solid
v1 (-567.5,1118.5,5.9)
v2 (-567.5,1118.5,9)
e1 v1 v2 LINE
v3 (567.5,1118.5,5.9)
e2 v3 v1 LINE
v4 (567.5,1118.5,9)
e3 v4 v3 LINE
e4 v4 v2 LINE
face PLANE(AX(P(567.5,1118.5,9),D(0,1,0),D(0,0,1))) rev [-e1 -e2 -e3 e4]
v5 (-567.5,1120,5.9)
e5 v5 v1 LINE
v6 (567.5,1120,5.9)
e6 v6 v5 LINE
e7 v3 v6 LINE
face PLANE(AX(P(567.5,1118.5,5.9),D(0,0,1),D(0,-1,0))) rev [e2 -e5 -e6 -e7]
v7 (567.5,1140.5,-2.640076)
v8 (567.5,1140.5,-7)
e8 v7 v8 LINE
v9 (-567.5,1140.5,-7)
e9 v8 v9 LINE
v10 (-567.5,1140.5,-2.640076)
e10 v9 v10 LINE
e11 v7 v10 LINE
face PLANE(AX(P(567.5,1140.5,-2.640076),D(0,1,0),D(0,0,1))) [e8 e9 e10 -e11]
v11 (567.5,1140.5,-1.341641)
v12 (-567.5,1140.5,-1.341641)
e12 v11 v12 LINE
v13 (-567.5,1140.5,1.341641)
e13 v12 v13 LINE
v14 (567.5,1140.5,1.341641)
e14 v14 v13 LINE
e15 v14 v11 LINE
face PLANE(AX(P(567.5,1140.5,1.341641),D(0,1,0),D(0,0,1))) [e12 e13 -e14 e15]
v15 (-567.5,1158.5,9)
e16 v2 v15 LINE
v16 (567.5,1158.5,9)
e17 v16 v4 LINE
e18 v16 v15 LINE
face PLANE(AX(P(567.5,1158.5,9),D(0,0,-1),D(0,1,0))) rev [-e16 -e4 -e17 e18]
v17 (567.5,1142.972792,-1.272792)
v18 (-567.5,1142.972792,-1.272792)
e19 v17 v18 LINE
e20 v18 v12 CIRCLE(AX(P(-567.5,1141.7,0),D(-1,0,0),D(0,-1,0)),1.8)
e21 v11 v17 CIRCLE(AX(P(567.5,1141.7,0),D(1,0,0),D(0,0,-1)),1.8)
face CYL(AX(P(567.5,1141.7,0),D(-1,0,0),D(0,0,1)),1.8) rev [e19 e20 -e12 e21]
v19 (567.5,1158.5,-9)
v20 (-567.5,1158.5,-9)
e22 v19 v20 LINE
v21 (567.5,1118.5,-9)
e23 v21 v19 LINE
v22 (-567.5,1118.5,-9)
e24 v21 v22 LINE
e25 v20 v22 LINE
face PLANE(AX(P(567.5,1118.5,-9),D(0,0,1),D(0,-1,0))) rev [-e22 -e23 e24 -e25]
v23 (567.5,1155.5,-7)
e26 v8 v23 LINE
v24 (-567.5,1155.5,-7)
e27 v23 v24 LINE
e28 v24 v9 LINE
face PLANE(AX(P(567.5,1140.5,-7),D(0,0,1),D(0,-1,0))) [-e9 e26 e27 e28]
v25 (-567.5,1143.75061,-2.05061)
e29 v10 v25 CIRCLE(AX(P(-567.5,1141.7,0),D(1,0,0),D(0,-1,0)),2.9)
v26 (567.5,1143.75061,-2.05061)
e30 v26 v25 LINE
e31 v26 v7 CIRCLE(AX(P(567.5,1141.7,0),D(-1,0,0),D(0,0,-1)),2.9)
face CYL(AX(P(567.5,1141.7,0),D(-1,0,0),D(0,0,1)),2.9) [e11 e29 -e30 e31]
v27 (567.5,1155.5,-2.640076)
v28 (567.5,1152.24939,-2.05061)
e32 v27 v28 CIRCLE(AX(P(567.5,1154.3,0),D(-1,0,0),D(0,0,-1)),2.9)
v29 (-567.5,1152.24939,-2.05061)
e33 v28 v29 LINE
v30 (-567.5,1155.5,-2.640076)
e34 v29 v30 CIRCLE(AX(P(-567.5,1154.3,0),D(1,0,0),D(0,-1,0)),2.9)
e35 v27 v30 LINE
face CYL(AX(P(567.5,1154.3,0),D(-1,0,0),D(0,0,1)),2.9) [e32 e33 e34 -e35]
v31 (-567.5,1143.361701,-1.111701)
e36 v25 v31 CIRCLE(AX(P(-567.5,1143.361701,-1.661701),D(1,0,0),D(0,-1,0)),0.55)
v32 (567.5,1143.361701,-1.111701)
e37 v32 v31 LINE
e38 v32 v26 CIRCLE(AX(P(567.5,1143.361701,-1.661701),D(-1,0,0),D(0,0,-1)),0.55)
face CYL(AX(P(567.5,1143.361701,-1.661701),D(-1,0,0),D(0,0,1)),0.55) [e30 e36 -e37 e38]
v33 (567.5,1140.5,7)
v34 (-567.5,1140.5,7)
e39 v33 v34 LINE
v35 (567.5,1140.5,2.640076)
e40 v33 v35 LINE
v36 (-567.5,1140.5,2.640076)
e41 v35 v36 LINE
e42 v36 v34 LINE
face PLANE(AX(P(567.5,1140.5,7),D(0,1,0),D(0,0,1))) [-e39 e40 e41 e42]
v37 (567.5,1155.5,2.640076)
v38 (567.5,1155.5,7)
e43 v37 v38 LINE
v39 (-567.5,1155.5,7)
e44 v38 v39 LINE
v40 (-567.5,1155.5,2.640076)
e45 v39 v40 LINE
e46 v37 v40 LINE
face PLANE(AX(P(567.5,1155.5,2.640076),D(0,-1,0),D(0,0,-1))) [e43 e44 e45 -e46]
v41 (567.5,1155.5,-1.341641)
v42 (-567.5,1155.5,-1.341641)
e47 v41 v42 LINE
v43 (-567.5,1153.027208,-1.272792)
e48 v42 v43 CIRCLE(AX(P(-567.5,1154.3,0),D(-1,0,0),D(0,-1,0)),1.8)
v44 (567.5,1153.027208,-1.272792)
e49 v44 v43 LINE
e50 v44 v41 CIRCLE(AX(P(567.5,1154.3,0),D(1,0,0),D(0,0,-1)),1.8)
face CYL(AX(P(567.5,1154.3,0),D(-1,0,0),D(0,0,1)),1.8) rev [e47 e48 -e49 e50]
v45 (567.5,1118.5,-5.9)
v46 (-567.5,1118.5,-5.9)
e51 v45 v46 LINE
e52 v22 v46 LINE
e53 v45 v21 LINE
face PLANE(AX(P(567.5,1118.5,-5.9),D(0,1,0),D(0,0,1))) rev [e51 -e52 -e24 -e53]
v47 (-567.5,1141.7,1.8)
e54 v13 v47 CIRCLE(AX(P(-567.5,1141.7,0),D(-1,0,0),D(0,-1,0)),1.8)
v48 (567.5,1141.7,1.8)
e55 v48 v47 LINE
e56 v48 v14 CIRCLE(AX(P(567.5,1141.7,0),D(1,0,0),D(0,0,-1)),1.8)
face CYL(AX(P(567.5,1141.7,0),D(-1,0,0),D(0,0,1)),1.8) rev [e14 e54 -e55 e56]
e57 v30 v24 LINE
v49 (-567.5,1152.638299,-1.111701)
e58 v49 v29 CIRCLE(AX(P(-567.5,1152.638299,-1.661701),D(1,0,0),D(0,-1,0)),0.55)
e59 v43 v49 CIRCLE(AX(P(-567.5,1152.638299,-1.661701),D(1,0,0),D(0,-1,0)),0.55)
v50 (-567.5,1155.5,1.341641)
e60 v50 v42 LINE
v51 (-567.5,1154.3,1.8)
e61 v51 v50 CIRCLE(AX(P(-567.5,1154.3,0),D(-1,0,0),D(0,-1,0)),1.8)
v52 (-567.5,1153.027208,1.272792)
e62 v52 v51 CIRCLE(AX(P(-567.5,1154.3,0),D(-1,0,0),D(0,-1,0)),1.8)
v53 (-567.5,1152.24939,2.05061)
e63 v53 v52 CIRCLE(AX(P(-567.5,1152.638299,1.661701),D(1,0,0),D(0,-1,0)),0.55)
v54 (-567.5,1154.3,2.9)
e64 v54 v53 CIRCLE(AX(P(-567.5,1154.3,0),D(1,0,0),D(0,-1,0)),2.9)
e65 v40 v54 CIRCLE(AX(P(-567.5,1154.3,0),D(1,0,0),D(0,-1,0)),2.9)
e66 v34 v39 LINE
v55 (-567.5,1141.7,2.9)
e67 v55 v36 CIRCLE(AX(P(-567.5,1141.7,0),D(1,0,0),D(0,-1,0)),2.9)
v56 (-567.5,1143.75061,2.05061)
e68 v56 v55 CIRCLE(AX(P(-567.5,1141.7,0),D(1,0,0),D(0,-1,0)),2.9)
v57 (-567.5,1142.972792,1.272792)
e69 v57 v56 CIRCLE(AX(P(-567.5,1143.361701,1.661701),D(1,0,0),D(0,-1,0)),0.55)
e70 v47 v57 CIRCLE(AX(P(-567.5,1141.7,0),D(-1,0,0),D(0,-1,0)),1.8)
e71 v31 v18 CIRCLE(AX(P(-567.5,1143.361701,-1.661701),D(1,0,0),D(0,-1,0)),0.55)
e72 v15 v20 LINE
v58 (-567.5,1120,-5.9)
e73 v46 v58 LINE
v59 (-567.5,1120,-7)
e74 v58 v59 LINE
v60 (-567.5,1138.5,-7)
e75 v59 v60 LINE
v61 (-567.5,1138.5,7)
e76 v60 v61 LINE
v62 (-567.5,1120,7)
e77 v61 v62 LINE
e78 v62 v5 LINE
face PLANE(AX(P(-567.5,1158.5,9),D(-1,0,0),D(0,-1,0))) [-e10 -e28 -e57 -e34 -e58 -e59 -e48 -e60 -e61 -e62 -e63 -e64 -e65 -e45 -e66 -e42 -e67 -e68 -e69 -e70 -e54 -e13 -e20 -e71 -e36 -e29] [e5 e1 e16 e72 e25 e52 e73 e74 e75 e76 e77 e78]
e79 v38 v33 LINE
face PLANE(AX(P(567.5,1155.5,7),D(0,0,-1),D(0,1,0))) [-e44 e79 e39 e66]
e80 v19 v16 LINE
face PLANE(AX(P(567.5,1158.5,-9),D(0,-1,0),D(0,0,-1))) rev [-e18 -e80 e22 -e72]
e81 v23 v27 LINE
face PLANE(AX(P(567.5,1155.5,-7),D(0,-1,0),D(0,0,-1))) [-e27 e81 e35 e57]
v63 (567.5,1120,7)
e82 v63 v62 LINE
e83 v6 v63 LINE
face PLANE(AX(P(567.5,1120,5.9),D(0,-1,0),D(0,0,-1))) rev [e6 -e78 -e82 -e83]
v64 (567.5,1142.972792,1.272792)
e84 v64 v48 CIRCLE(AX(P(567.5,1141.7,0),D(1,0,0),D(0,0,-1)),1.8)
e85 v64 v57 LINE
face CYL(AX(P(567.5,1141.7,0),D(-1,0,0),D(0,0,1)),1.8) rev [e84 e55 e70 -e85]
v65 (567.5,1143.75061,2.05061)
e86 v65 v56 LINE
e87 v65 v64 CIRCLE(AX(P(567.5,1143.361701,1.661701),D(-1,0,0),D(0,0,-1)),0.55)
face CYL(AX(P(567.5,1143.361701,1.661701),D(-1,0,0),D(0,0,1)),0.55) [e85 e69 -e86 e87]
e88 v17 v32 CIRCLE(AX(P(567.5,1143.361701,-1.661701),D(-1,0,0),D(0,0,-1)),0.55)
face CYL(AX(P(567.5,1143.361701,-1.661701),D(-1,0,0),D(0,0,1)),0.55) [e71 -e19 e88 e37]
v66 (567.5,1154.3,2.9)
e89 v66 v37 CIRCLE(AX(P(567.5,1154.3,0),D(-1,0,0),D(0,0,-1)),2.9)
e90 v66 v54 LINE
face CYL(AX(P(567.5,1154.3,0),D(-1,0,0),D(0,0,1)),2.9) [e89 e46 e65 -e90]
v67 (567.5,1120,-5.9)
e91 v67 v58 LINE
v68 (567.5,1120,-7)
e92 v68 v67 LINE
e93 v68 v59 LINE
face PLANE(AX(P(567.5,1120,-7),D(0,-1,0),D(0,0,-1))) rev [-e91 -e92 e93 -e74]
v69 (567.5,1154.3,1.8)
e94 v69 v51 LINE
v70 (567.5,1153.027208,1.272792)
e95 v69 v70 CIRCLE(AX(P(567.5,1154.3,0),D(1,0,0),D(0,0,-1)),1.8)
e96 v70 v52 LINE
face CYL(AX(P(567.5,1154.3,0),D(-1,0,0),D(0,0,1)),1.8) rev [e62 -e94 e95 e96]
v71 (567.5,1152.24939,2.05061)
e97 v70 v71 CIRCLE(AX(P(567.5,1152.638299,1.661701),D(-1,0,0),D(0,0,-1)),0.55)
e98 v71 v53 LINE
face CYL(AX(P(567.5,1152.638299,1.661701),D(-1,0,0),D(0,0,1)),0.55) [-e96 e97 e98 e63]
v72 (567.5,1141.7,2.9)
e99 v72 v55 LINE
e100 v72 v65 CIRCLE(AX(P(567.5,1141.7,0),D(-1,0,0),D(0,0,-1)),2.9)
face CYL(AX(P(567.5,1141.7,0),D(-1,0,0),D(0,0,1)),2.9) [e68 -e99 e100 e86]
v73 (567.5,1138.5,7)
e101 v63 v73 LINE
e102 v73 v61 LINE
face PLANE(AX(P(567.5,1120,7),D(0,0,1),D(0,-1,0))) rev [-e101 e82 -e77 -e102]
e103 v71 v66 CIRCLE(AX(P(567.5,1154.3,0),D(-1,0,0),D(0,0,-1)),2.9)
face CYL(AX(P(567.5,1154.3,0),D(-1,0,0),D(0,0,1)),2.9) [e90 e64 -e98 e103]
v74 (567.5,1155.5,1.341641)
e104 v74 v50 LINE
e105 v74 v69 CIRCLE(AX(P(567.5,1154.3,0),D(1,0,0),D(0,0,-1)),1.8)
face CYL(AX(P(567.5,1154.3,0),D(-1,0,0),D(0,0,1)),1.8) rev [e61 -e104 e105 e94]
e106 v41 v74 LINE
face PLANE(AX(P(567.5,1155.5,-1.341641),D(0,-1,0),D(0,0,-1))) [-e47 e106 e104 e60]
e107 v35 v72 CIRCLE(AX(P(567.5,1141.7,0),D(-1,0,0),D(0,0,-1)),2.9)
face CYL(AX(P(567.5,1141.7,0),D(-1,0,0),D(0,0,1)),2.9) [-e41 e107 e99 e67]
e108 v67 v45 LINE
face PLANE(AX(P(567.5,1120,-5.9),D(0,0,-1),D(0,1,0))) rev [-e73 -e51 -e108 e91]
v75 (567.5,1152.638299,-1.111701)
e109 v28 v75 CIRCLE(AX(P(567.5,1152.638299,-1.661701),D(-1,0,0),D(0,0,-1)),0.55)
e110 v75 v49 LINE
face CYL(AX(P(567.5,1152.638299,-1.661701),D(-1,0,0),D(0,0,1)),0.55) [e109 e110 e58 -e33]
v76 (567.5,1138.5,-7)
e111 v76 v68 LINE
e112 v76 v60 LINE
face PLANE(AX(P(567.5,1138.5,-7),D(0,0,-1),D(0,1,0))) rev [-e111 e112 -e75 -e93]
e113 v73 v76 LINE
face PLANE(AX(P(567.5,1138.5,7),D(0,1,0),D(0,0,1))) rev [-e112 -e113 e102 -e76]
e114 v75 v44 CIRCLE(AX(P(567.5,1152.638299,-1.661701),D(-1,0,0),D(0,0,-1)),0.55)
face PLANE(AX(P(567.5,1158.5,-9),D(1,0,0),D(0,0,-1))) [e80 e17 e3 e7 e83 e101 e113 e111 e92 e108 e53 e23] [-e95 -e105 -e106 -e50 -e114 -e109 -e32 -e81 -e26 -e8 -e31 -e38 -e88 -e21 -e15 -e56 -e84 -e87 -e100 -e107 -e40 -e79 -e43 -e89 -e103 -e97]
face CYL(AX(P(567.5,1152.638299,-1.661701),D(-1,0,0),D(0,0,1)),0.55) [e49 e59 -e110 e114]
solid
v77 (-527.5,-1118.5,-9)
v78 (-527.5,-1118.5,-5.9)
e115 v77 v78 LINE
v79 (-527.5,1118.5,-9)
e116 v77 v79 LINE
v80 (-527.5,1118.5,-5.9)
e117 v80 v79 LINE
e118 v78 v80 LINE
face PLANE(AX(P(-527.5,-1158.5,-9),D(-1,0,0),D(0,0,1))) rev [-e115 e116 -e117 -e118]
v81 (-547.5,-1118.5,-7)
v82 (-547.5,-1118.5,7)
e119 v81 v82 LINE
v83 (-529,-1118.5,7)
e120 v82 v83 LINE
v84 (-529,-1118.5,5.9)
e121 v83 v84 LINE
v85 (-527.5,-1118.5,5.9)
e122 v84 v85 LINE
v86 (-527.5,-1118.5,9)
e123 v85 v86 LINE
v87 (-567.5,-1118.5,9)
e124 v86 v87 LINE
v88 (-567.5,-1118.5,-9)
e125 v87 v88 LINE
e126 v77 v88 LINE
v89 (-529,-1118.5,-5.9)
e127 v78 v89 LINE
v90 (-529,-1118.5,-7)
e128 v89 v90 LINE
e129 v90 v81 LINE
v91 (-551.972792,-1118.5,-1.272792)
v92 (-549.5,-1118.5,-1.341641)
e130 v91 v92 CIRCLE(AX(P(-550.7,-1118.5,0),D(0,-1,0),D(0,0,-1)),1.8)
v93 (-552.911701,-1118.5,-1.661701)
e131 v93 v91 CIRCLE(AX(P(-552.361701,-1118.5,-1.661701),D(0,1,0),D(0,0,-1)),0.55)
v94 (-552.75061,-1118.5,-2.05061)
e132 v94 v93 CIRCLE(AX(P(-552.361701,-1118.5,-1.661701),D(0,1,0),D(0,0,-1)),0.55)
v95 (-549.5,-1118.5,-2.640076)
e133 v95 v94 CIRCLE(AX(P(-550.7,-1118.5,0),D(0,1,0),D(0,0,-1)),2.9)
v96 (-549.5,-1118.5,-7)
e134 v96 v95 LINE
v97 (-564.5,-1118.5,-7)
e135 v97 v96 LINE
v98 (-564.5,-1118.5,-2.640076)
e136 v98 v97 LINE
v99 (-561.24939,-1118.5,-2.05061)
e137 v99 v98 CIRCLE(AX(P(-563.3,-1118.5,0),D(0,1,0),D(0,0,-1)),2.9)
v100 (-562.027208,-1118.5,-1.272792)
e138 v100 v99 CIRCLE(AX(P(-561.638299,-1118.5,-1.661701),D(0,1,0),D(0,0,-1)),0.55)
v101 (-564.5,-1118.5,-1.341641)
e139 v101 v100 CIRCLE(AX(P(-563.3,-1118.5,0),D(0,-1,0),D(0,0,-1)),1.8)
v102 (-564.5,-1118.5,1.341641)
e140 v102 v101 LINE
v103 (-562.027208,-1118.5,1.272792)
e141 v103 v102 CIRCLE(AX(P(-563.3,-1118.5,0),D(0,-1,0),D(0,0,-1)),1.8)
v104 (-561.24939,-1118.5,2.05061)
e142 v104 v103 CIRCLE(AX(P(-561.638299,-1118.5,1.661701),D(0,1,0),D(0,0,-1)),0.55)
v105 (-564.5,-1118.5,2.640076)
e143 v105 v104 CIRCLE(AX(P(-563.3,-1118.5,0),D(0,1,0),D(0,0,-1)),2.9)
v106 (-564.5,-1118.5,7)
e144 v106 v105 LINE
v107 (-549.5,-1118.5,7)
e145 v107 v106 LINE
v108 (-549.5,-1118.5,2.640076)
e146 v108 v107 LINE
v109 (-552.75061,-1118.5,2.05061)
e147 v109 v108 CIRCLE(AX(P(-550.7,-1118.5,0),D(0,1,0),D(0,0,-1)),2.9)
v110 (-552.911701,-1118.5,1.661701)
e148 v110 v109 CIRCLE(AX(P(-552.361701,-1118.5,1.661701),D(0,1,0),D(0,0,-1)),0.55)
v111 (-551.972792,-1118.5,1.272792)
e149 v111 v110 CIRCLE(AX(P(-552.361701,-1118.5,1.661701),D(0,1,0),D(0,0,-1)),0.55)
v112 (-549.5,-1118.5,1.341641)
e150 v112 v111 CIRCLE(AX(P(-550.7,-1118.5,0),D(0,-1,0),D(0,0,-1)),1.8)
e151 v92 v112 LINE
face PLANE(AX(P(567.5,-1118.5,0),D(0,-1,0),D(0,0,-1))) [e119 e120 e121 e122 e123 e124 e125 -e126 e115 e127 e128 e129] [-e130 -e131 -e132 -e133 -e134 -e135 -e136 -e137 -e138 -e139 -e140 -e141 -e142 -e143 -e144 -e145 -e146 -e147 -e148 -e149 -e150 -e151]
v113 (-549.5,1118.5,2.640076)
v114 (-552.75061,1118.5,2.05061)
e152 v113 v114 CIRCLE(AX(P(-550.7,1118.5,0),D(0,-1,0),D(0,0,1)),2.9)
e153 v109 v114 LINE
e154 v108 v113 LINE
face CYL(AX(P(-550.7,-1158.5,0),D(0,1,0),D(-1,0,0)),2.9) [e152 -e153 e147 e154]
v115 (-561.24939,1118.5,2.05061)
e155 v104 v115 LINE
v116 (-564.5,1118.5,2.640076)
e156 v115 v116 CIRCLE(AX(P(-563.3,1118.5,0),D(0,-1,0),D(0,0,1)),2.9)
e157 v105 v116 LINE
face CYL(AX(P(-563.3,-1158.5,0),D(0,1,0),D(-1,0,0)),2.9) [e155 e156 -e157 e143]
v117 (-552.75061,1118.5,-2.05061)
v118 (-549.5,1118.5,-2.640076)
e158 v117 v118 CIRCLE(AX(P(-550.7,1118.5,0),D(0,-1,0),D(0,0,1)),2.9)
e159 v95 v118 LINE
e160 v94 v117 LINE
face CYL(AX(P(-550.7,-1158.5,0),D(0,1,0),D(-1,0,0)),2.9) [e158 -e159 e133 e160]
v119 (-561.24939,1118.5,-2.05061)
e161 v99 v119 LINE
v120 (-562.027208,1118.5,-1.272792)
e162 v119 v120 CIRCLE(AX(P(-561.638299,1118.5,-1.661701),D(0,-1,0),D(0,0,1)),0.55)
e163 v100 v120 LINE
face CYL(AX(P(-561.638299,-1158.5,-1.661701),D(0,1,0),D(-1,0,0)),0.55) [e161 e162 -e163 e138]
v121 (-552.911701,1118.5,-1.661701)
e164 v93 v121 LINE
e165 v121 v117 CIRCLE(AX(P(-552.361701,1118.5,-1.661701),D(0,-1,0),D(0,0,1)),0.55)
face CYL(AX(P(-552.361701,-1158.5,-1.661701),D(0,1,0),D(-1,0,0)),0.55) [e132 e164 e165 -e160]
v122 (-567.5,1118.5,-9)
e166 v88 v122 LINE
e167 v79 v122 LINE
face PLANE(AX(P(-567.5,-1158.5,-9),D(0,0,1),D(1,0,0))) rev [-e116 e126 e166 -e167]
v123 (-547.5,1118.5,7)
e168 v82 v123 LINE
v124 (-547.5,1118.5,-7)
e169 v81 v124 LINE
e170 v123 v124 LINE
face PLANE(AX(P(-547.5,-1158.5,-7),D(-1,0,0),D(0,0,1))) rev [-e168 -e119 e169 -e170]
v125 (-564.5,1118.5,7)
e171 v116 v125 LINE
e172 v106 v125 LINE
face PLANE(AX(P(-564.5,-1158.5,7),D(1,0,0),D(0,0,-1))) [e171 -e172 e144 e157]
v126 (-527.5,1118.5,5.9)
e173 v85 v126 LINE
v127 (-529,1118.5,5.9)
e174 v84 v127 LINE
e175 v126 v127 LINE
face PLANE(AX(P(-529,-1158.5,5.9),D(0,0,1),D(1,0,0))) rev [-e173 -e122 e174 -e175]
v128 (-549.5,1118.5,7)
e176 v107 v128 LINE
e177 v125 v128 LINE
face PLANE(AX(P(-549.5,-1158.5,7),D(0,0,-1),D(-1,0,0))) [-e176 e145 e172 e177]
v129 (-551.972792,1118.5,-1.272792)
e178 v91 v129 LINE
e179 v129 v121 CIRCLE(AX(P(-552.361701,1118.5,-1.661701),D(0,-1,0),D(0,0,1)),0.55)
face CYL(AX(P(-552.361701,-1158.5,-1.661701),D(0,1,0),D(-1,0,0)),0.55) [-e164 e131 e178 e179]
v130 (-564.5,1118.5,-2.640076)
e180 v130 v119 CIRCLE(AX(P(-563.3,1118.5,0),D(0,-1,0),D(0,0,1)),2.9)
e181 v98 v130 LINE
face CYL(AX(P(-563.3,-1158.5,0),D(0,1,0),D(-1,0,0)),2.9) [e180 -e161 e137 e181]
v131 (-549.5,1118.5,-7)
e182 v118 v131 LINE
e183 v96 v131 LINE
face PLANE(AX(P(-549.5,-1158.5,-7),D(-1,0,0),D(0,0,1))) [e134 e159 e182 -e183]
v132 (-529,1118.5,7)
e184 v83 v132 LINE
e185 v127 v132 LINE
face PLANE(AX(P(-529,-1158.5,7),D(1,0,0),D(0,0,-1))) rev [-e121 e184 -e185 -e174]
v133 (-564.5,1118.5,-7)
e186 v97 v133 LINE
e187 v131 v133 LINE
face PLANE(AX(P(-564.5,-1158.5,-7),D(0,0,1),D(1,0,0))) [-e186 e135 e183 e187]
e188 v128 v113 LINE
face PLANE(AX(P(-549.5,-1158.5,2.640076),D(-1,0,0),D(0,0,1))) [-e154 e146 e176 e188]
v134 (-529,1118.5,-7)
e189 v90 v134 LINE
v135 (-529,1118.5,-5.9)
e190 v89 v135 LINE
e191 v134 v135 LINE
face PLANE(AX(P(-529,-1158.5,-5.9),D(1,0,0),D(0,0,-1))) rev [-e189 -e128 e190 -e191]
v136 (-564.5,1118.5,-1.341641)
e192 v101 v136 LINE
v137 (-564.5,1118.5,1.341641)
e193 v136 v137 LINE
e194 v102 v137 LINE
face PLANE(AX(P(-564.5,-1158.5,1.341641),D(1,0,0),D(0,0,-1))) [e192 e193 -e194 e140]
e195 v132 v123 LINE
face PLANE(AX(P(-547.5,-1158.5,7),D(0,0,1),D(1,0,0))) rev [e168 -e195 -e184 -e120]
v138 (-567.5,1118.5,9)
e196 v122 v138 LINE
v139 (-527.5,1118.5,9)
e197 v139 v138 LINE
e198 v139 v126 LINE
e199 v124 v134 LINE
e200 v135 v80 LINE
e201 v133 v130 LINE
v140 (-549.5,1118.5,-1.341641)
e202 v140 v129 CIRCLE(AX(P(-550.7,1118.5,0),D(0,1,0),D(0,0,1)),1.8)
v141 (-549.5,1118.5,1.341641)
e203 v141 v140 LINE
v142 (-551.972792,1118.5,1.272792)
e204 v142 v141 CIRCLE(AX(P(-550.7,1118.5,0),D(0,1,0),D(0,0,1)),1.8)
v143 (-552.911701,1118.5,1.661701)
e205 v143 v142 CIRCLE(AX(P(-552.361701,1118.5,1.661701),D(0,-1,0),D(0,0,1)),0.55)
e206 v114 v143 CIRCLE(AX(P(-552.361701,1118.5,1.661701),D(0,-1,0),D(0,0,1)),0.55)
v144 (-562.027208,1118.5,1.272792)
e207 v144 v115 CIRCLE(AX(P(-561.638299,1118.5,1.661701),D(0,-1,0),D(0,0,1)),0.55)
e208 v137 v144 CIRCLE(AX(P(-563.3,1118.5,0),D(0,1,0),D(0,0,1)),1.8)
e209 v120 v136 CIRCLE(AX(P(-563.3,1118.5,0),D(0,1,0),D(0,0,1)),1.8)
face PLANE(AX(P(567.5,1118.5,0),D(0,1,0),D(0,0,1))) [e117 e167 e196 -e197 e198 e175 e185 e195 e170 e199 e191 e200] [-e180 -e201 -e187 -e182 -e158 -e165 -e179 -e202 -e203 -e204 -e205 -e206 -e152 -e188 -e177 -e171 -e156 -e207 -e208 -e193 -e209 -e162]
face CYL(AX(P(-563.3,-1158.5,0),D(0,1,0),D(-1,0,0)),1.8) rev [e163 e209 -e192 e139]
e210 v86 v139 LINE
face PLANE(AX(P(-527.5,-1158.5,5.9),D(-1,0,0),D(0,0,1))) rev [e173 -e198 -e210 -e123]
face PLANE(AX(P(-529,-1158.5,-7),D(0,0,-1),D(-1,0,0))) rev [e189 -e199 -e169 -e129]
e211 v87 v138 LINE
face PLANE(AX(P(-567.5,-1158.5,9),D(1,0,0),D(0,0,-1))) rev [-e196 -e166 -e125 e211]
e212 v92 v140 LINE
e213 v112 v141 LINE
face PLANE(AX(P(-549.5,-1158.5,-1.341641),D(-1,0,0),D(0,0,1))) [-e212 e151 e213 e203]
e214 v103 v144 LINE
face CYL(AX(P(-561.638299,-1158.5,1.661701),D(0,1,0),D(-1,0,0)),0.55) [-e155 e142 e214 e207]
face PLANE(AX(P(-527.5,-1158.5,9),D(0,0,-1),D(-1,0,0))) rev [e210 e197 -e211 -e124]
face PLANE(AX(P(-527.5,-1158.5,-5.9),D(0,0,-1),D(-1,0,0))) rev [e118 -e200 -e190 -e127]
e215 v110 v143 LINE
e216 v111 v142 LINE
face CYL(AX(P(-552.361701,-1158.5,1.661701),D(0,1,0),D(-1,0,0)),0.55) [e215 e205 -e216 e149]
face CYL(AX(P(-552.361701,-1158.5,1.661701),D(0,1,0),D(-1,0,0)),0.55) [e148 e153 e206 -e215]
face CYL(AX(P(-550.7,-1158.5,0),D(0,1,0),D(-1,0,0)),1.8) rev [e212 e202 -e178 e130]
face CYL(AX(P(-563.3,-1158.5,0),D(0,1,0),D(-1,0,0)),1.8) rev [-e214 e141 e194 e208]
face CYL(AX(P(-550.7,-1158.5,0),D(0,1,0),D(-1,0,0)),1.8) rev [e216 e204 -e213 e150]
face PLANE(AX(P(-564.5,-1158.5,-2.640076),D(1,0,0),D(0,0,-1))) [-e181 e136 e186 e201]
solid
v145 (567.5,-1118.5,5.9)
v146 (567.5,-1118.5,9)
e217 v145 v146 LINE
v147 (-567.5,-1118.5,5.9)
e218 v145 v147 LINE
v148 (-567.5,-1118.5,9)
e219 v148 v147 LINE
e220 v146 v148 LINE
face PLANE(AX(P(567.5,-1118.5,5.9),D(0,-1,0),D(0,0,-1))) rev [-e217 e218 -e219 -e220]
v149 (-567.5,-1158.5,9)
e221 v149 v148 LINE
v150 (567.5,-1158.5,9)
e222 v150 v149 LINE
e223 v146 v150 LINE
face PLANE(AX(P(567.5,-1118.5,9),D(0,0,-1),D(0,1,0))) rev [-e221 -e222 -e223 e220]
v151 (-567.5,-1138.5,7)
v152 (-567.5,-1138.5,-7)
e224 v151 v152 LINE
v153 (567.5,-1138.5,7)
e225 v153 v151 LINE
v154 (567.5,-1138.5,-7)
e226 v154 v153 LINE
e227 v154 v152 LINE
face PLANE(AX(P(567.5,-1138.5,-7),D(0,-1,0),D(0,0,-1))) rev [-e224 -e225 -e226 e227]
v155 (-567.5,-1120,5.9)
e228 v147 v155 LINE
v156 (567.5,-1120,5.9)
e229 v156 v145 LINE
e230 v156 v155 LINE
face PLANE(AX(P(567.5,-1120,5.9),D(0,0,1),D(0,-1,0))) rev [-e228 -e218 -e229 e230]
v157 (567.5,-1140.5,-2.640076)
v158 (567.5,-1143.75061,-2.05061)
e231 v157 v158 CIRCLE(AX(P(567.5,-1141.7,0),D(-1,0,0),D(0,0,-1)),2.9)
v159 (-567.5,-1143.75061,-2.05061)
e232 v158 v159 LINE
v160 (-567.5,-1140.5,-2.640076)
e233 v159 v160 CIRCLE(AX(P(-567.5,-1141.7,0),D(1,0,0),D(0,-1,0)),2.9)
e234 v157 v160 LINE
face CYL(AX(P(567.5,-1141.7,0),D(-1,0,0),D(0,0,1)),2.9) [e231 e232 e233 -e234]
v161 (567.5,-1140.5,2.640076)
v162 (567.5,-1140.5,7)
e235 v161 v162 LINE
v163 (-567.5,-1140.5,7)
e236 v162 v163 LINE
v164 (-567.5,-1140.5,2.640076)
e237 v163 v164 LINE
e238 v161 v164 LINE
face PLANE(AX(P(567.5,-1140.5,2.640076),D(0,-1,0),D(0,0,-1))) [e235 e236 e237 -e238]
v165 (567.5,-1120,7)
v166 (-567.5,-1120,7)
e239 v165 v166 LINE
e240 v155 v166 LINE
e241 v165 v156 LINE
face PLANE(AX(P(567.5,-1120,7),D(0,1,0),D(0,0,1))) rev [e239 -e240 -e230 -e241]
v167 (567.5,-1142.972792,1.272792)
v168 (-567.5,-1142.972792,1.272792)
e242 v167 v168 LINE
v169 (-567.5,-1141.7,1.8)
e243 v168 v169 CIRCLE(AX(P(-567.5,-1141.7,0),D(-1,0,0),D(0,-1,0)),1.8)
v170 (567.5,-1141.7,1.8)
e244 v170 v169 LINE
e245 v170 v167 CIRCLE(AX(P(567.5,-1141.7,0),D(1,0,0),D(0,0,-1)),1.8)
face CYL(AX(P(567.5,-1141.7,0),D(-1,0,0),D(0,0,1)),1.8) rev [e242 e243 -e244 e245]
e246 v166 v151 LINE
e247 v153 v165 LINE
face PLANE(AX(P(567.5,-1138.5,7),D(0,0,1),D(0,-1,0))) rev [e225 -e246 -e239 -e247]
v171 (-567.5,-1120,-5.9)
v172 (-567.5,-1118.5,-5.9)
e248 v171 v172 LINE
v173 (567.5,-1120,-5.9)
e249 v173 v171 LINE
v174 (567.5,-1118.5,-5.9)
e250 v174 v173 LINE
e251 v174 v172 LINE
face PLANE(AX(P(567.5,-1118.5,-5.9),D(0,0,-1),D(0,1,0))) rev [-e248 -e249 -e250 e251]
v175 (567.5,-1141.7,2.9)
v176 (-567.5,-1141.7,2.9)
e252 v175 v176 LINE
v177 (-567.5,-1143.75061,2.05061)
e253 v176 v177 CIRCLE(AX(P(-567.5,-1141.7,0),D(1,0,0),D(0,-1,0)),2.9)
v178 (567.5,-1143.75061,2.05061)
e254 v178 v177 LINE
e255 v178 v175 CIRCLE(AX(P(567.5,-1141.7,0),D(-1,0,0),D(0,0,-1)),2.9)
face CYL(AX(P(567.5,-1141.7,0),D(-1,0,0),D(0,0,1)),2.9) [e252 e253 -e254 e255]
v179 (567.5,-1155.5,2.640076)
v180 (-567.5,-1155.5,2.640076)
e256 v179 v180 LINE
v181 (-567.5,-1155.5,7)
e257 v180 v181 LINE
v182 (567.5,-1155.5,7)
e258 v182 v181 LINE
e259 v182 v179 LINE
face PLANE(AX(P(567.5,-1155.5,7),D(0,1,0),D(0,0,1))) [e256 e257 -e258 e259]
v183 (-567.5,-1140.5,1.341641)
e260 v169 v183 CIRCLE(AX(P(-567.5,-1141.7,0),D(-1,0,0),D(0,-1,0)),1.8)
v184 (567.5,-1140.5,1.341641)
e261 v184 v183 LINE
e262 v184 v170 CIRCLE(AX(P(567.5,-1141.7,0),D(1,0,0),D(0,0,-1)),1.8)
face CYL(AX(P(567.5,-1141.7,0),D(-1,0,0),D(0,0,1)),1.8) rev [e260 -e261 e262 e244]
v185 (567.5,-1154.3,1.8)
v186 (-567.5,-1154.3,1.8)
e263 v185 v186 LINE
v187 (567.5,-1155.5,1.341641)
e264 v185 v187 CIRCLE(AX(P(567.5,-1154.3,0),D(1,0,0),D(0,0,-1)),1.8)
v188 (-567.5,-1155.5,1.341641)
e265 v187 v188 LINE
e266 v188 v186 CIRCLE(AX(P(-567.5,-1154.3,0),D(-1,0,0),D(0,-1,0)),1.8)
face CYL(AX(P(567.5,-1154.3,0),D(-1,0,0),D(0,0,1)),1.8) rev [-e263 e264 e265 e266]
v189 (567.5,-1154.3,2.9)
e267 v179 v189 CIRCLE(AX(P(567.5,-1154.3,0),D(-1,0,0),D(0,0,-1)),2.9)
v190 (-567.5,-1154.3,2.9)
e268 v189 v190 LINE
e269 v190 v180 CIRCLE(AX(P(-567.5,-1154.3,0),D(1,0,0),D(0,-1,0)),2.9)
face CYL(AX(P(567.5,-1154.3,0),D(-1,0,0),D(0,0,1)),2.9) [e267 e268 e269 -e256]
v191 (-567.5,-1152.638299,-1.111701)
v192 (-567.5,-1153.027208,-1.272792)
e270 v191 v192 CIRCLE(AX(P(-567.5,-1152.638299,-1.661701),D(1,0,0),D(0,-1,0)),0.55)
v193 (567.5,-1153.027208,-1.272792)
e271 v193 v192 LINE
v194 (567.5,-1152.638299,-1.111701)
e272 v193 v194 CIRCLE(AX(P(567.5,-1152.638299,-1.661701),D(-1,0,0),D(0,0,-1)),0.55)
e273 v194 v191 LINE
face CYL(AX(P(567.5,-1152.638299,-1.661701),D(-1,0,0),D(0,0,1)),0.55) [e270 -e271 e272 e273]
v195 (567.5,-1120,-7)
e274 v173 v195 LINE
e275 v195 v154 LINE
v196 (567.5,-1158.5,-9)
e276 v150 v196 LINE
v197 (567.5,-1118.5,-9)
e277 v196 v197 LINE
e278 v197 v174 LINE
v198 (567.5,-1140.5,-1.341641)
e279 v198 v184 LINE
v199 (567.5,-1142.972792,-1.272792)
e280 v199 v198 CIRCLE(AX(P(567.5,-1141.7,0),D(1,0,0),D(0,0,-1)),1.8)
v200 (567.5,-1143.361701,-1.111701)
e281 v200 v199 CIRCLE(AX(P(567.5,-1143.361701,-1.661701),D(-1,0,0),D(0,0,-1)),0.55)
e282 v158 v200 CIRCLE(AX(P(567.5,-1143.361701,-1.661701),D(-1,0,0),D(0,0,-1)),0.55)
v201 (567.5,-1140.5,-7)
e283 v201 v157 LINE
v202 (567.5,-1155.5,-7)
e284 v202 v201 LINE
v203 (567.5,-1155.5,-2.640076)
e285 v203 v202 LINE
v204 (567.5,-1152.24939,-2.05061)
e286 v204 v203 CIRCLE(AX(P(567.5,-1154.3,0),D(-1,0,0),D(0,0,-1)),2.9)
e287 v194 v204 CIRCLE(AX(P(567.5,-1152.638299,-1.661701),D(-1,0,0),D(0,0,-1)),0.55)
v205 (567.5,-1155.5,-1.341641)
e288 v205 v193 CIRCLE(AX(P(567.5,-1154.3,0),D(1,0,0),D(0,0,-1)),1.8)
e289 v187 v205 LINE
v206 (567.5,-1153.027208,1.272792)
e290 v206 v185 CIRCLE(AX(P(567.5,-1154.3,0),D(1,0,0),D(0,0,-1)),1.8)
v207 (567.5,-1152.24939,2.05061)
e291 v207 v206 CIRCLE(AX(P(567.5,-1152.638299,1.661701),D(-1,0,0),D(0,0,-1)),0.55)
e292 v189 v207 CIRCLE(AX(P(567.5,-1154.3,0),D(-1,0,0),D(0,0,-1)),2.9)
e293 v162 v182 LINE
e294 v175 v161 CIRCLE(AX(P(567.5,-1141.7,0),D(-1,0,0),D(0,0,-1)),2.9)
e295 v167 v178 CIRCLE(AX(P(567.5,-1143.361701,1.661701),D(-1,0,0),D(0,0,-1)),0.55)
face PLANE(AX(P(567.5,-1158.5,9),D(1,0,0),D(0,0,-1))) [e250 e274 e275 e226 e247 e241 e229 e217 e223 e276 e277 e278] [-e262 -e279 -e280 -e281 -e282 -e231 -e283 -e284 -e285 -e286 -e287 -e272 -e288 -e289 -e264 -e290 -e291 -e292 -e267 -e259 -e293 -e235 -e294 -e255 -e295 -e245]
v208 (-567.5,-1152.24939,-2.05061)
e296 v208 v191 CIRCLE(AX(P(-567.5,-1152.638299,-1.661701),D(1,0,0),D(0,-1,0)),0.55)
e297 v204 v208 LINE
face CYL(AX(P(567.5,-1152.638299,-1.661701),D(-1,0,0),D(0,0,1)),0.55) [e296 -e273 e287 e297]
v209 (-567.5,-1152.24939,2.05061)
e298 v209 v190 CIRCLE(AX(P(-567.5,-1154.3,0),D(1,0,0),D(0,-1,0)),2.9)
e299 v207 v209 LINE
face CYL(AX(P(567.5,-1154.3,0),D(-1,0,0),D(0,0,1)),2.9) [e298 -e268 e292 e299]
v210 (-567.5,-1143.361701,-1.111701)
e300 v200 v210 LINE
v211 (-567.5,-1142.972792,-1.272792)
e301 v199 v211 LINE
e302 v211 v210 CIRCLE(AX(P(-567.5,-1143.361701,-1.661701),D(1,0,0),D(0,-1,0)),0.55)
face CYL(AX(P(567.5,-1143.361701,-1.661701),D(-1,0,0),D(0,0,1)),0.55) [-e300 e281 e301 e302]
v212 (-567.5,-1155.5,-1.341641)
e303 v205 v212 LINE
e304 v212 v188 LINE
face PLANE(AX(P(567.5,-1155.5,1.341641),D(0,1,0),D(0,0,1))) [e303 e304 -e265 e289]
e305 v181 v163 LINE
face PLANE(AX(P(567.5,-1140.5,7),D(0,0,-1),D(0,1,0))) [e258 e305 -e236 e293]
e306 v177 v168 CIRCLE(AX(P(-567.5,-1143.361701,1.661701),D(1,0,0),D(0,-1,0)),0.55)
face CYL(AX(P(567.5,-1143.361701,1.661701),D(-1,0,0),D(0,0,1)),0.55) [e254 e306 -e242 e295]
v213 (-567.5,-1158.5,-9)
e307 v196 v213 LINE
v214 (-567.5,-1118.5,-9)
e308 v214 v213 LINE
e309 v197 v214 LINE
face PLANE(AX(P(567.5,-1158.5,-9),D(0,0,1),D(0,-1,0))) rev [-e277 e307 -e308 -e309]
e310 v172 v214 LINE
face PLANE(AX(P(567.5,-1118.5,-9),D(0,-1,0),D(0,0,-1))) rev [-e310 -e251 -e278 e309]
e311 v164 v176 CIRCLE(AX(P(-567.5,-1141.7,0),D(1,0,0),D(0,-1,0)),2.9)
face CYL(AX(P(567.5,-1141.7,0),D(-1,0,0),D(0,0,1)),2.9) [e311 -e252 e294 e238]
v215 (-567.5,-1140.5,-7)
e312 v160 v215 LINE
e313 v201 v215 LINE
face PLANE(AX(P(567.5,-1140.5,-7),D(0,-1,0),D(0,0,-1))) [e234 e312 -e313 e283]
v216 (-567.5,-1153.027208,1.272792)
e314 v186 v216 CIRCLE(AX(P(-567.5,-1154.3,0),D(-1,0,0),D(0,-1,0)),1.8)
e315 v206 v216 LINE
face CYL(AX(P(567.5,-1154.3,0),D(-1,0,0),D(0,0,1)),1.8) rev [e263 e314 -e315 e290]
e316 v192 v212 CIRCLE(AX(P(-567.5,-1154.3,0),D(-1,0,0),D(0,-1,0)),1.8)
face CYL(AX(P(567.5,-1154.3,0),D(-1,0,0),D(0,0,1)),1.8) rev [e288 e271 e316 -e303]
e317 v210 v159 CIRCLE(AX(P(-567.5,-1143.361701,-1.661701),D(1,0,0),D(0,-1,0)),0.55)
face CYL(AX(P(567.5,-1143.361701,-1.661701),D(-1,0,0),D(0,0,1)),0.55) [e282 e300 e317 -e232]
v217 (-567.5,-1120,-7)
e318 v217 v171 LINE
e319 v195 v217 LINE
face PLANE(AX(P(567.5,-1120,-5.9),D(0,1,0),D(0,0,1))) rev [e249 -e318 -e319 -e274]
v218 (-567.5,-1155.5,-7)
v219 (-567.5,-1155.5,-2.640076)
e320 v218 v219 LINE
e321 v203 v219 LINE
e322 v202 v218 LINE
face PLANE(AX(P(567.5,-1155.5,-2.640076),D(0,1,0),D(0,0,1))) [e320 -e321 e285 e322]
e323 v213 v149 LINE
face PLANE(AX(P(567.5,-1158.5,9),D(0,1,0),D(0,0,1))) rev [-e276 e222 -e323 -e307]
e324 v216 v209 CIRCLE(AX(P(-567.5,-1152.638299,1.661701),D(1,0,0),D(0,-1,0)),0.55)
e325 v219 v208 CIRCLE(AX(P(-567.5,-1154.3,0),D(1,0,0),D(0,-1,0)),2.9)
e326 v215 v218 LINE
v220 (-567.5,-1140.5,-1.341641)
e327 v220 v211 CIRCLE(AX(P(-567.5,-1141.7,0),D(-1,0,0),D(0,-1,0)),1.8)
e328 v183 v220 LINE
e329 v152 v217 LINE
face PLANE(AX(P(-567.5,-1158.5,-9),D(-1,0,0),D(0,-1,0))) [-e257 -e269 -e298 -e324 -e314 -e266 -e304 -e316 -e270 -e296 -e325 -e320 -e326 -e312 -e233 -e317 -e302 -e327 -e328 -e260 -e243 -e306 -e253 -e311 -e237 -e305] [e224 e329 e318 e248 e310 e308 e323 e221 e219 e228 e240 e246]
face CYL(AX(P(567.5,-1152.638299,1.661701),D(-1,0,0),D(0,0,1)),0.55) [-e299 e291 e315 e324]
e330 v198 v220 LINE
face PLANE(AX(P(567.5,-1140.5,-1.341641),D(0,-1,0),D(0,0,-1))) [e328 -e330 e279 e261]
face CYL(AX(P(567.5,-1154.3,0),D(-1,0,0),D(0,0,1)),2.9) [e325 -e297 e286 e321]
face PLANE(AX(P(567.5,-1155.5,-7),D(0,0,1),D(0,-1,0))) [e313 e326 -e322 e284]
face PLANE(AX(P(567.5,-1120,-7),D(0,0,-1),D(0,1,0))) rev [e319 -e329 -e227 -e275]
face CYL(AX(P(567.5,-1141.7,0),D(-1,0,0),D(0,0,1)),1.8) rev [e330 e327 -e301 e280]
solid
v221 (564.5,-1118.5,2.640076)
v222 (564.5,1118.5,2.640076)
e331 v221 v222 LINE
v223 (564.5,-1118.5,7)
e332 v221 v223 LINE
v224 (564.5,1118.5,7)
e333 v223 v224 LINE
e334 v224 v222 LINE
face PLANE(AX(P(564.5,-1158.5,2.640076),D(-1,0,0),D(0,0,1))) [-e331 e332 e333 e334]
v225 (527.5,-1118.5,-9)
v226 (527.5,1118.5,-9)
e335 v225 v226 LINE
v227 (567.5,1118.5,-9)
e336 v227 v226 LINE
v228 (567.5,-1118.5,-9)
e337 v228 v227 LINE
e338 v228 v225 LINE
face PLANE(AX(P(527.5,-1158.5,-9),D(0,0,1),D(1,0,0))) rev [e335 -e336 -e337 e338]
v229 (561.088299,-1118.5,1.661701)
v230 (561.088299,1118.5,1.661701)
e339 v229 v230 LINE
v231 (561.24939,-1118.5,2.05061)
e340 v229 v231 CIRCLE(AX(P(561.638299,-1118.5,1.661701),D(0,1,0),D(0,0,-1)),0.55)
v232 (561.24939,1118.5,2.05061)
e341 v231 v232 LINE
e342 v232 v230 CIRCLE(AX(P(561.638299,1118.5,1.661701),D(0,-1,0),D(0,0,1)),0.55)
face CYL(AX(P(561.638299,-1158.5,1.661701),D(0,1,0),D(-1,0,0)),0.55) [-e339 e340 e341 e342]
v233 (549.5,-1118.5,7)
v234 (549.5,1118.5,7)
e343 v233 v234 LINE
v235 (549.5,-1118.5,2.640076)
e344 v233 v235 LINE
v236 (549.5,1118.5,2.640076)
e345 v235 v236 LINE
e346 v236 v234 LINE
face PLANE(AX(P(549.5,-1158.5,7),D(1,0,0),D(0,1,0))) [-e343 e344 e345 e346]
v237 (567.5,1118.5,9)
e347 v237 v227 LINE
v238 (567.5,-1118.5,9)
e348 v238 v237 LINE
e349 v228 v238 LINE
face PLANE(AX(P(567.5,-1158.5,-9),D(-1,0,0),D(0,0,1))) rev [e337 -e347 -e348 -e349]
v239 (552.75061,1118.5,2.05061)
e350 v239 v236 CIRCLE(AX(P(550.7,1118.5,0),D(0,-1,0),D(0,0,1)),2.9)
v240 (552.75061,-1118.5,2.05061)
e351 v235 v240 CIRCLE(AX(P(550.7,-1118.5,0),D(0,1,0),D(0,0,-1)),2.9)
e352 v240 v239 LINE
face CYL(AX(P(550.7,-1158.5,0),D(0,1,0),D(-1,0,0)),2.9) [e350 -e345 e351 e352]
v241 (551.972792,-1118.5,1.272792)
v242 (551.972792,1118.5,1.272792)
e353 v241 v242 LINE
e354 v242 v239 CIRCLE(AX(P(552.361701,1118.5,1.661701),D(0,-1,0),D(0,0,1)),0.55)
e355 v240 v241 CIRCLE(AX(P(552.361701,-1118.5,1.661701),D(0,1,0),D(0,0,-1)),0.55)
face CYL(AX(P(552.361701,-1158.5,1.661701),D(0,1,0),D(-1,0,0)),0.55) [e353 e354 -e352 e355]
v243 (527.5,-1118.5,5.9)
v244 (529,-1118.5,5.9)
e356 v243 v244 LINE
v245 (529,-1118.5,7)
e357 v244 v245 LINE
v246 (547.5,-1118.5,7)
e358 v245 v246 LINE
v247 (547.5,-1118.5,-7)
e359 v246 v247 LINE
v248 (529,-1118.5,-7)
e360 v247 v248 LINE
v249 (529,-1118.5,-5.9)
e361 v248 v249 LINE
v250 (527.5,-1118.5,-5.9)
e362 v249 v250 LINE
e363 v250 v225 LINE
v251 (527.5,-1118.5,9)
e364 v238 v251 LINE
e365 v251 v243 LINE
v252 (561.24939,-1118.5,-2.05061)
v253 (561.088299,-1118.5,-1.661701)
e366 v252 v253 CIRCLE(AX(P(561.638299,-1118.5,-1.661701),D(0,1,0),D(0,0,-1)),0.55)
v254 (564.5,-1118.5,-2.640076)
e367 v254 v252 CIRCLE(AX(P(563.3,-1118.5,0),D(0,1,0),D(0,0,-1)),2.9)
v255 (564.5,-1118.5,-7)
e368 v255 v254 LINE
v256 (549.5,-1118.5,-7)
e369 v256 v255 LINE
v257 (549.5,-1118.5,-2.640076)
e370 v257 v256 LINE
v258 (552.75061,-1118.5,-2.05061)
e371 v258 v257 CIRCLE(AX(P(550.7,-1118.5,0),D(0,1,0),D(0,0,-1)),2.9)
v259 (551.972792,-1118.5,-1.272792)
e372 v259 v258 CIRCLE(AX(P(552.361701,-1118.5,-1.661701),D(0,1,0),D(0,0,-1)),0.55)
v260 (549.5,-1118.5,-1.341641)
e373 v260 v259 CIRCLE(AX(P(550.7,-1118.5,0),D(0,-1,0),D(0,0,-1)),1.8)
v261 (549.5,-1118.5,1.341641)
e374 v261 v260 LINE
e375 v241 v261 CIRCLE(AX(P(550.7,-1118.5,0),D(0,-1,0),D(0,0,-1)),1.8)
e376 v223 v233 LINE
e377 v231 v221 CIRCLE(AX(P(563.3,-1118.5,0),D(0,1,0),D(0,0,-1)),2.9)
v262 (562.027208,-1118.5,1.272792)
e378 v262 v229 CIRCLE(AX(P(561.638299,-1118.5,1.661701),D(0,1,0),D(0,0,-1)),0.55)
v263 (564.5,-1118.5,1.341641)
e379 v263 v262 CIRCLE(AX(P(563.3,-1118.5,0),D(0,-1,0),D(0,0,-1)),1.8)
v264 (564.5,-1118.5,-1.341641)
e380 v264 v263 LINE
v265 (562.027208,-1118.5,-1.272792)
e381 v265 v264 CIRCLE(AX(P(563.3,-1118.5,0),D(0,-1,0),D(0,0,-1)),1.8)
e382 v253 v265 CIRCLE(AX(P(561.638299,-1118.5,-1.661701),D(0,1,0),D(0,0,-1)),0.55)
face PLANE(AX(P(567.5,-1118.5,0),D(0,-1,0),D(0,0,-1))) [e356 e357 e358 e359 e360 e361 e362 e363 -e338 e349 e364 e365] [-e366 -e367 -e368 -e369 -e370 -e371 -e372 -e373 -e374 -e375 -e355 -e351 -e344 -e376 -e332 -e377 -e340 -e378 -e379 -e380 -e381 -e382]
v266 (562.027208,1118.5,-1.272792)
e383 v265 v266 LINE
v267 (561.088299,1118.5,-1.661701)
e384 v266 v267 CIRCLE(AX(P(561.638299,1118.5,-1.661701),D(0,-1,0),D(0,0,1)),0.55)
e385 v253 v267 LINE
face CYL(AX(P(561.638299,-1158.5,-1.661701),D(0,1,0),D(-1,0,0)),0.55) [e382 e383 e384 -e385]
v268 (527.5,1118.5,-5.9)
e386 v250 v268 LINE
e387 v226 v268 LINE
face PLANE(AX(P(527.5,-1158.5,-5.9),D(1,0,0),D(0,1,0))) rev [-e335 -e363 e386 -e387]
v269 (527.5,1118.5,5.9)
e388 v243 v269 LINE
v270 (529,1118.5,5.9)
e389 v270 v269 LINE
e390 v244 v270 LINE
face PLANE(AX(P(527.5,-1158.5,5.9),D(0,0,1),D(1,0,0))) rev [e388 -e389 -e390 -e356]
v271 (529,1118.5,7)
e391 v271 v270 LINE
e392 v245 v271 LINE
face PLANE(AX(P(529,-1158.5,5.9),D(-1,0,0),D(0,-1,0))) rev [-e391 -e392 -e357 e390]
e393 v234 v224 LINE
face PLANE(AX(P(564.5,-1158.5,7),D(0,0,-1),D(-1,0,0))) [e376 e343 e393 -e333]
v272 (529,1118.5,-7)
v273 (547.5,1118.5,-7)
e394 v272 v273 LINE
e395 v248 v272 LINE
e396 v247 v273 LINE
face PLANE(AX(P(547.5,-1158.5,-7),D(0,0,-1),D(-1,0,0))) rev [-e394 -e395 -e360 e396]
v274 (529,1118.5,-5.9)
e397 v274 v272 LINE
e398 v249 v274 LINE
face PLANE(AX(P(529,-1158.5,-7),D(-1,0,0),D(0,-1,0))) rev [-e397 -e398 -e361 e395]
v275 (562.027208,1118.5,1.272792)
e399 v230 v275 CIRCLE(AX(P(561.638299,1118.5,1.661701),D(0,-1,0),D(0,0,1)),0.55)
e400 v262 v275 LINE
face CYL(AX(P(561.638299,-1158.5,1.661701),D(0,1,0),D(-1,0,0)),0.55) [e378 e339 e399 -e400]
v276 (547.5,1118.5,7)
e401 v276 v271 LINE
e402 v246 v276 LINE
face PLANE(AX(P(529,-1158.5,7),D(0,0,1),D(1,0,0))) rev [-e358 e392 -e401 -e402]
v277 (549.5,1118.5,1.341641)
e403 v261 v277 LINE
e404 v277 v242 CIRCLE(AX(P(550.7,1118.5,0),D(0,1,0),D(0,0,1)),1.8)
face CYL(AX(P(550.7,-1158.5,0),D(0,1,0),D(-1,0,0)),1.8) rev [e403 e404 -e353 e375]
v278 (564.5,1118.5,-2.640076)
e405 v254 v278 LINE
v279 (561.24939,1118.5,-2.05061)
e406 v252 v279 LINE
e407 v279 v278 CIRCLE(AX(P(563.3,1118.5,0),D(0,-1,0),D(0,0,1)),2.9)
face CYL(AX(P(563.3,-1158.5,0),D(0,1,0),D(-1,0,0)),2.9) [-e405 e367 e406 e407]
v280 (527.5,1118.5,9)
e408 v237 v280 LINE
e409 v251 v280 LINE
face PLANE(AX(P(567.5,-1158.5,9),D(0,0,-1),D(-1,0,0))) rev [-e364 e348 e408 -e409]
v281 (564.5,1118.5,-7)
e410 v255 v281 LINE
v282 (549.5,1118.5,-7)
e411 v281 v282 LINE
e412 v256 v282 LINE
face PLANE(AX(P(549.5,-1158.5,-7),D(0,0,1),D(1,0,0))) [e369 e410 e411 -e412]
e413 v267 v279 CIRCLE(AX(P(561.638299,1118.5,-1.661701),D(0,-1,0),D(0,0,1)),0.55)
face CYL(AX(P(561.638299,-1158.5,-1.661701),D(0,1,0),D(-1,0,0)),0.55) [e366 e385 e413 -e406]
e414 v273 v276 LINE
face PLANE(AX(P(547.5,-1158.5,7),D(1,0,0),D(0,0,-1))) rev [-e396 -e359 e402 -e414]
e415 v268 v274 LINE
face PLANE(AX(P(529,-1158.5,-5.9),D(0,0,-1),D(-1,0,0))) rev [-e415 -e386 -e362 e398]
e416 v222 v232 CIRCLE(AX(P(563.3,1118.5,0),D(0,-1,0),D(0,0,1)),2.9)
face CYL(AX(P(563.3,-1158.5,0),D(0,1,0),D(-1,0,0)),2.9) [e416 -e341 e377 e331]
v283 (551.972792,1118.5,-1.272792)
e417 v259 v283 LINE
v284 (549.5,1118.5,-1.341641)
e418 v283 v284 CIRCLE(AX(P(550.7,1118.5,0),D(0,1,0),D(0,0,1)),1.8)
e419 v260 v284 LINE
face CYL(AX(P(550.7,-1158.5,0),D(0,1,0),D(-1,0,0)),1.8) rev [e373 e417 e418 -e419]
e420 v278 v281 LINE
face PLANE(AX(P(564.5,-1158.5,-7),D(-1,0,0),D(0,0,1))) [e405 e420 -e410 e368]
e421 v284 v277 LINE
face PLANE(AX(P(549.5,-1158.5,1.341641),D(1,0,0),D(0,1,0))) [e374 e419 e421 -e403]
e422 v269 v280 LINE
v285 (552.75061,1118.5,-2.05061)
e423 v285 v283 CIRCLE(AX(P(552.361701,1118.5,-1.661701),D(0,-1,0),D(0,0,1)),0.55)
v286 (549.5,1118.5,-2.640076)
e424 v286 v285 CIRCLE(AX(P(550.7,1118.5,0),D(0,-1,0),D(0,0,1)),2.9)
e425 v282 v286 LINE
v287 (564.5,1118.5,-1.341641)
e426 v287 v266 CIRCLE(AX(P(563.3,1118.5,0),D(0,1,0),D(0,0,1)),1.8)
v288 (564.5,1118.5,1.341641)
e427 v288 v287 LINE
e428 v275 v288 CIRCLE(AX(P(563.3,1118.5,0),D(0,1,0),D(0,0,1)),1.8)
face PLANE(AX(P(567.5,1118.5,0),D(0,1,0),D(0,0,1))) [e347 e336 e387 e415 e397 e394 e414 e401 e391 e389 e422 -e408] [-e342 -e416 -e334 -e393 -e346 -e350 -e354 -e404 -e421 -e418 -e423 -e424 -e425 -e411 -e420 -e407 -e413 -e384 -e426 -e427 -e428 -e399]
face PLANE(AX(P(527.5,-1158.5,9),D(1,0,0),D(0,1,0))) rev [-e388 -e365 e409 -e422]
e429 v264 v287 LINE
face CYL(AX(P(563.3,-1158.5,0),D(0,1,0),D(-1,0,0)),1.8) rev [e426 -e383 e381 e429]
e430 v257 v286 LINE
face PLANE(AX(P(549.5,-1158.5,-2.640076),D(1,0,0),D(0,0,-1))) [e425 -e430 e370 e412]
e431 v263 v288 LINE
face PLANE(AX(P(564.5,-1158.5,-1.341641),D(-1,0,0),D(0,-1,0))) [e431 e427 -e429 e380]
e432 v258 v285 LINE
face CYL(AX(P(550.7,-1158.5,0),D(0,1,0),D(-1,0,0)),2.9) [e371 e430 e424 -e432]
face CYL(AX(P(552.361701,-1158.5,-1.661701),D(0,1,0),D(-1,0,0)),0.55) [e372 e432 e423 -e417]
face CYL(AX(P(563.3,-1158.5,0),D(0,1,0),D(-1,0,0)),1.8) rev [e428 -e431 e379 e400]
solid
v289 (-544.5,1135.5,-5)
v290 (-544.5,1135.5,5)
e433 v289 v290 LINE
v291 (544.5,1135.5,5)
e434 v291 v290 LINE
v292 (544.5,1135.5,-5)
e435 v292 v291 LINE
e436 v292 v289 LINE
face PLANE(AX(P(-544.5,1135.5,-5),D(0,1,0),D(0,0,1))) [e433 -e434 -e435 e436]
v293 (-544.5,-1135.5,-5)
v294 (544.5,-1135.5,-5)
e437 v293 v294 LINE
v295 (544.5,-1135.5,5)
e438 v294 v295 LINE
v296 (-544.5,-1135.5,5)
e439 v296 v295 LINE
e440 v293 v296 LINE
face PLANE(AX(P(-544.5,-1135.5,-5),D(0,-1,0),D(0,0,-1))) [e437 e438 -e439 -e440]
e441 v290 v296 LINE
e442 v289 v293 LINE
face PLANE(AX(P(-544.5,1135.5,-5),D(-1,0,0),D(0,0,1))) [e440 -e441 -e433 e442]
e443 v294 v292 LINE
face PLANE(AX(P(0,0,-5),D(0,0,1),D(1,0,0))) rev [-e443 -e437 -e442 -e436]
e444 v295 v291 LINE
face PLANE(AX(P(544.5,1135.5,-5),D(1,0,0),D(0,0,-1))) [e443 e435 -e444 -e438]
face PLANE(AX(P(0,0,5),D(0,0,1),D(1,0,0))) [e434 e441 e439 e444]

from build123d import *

# Parameters (mm, degrees)
MEMBER_1_DEPTH   = 1135
MEMBER_1_2_DEPTH = 1135
MEMBER_1_3_DEPTH = 2319
MEMBER_1_4_DEPTH = 2319
EXTRUDE_START    = -4
SKETCH_2_W       = 1089
SKETCH_2_H       = 2271
EXTRUDE_1_DEPTH  = 10


with BuildPart() as part:
    # Sketch1 → Member 1 (new body)
    with BuildSketch(Plane(origin=(-567.5, 1158.5, 0), x_dir=(0, 0, -1), z_dir=(1, 0, 0))):
        Polygon((7, -38.5), (5.9, -38.5), (5.9, -40), (7, -40), (9, -40), (9, 0), (-9, 0), (-9, -40), (-7, -40), (-5.9, -40), (-5.9, -38.5), (-7, -38.5), (-7, -20), (7, -20), align=None)
        with BuildLine():
            Line((-1.341640786, -18), (1.341640786, -18))
            ThreePointArc((1.341640786, -18), (1.799302724, -16.749903013), (1.272792206, -15.527207794))
            ThreePointArc((1.272792206, -15.527207794), (1.272792206, -14.749390335), (2.050609665, -14.749390335))
            ThreePointArc((2.050609665, -14.749390335), (2.853462499, -16.282552641), (2.640075756, -18))
            Line((2.640075756, -18), (7, -18))
            Line((7, -18), (7, -3))
            Line((7, -3), (2.640075756, -3))
            ThreePointArc((2.640075756, -3), (2.853462499, -4.717447359), (2.050609665, -6.250609665))
            ThreePointArc((2.050609665, -6.250609665), (1.272792206, -6.250609665), (1.272792206, -5.472792206))
            ThreePointArc((1.272792206, -5.472792206), (1.799302724, -4.250096987), (1.341640786, -3))
            Line((1.341640786, -3), (-1.341640786, -3))
            ThreePointArc((-1.341640786, -3), (-1.799302724, -4.250096987), (-1.272792206, -5.472792206))
            ThreePointArc((-1.272792206, -5.472792206), (-1.272792206, -6.250609665), (-2.050609665, -6.250609665))
            ThreePointArc((-2.050609665, -6.250609665), (-2.853462499, -4.717447359), (-2.640075756, -3))
            Line((-2.640075756, -3), (-7, -3))
            Line((-7, -3), (-7, -18))
            Line((-7, -18), (-2.640075756, -18))
            ThreePointArc((-2.640075756, -18), (-2.853462499, -16.282552641), (-2.050609665, -14.749390335))
            ThreePointArc((-2.050609665, -14.749390335), (-1.272792206, -14.749390335), (-1.272792206, -15.527207794))
            ThreePointArc((-1.272792206, -15.527207794), (-1.799302724, -16.749903013), (-1.341640786, -18))
        make_face(mode=Mode.SUBTRACT)
    extrude(amount=MEMBER_1_DEPTH)


with BuildPart() as body_2:
    # Sketch1 on segment 2 (carried to segment 2) → Member 1 2 (new body)
    with BuildSketch(Plane(origin=(-567.5, -1158.5, 0), x_dir=(0, 0, 1), z_dir=(1, 0, 0))):
        Polygon((7, -38.5), (5.9, -38.5), (5.9, -40), (7, -40), (9, -40), (9, 0), (-9, 0), (-9, -40), (-7, -40), (-5.9, -40), (-5.9, -38.5), (-7, -38.5), (-7, -20), (7, -20), align=None)
        with BuildLine():
            Line((-1.341640786, -18), (1.341640786, -18))
            ThreePointArc((1.341640786, -18), (1.799302724, -16.749903013), (1.272792206, -15.527207794))
            ThreePointArc((1.272792206, -15.527207794), (1.272792206, -14.749390335), (2.050609665, -14.749390335))
            ThreePointArc((2.050609665, -14.749390335), (2.853462499, -16.282552641), (2.640075756, -18))
            Line((2.640075756, -18), (7, -18))
            Line((7, -18), (7, -3))
            Line((7, -3), (2.640075756, -3))
            ThreePointArc((2.640075756, -3), (2.853462499, -4.717447359), (2.050609665, -6.250609665))
            ThreePointArc((2.050609665, -6.250609665), (1.272792206, -6.250609665), (1.272792206, -5.472792206))
            ThreePointArc((1.272792206, -5.472792206), (1.799302724, -4.250096987), (1.341640786, -3))
            Line((1.341640786, -3), (-1.341640786, -3))
            ThreePointArc((-1.341640786, -3), (-1.799302724, -4.250096987), (-1.272792206, -5.472792206))
            ThreePointArc((-1.272792206, -5.472792206), (-1.272792206, -6.250609665), (-2.050609665, -6.250609665))
            ThreePointArc((-2.050609665, -6.250609665), (-2.853462499, -4.717447359), (-2.640075756, -3))
            Line((-2.640075756, -3), (-7, -3))
            Line((-7, -3), (-7, -18))
            Line((-7, -18), (-2.640075756, -18))
            ThreePointArc((-2.640075756, -18), (-2.853462499, -16.282552641), (-2.050609665, -14.749390335))
            ThreePointArc((-2.050609665, -14.749390335), (-1.272792206, -14.749390335), (-1.272792206, -15.527207794))
            ThreePointArc((-1.272792206, -15.527207794), (-1.799302724, -16.749903013), (-1.341640786, -18))
        make_face(mode=Mode.SUBTRACT)
    extrude(amount=MEMBER_1_2_DEPTH)


with BuildPart() as body_3:
    # Sketch1 on segment 3 (carried to segment 3) → Member 1 3 (new body)
    with BuildSketch(Plane(origin=(567.5, 1159.5, 0), x_dir=(0, 0, -1), z_dir=(0, -1, 0))):
        Polygon((7, -38.5), (5.9, -38.5), (5.9, -40), (7, -40), (9, -40), (9, 0), (-9, 0), (-9, -40), (-7, -40), (-5.9, -40), (-5.9, -38.5), (-7, -38.5), (-7, -20), (7, -20), align=None)
        with BuildLine():
            Line((-1.341640786, -18), (1.341640786, -18))
            ThreePointArc((1.341640786, -18), (1.799302724, -16.749903013), (1.272792206, -15.527207794))
            ThreePointArc((1.272792206, -15.527207794), (1.272792206, -14.749390335), (2.050609665, -14.749390335))
            ThreePointArc((2.050609665, -14.749390335), (2.853462499, -16.282552641), (2.640075756, -18))
            Line((2.640075756, -18), (7, -18))
            Line((7, -18), (7, -3))
            Line((7, -3), (2.640075756, -3))
            ThreePointArc((2.640075756, -3), (2.853462499, -4.717447359), (2.050609665, -6.250609665))
            ThreePointArc((2.050609665, -6.250609665), (1.272792206, -6.250609665), (1.272792206, -5.472792206))
            ThreePointArc((1.272792206, -5.472792206), (1.799302724, -4.250096987), (1.341640786, -3))
            Line((1.341640786, -3), (-1.341640786, -3))
            ThreePointArc((-1.341640786, -3), (-1.799302724, -4.250096987), (-1.272792206, -5.472792206))
            ThreePointArc((-1.272792206, -5.472792206), (-1.272792206, -6.250609665), (-2.050609665, -6.250609665))
            ThreePointArc((-2.050609665, -6.250609665), (-2.853462499, -4.717447359), (-2.640075756, -3))
            Line((-2.640075756, -3), (-7, -3))
            Line((-7, -3), (-7, -18))
            Line((-7, -18), (-2.640075756, -18))
            ThreePointArc((-2.640075756, -18), (-2.853462499, -16.282552641), (-2.050609665, -14.749390335))
            ThreePointArc((-2.050609665, -14.749390335), (-1.272792206, -14.749390335), (-1.272792206, -15.527207794))
            ThreePointArc((-1.272792206, -15.527207794), (-1.799302724, -16.749903013), (-1.341640786, -18))
        make_face(mode=Mode.SUBTRACT)
    extrude(amount=MEMBER_1_3_DEPTH)

    # Member 1 3 end butt 1
    split(bisect_by=Plane(origin=(567.5, 1118.5, 0), x_dir=(1, 0, 0), z_dir=(0, -1, 0)), keep=Keep.TOP)

    # Member 1 3 end butt 2
    split(bisect_by=Plane(origin=(567.5, -1118.5, 0), x_dir=(-1, 0, 0), z_dir=(0, 1, 0)), keep=Keep.TOP)


with BuildPart() as body_4:
    # Sketch1 on segment 4 (carried to segment 4) → Member 1 4 (new body)
    with BuildSketch(Plane(origin=(-567.5, 1159.5, 0), x_dir=(0, 0, 1), z_dir=(0, -1, 0))):
        Polygon((7, -38.5), (5.9, -38.5), (5.9, -40), (7, -40), (9, -40), (9, 0), (-9, 0), (-9, -40), (-7, -40), (-5.9, -40), (-5.9, -38.5), (-7, -38.5), (-7, -20), (7, -20), align=None)
        with BuildLine():
            Line((-1.341640786, -18), (1.341640786, -18))
            ThreePointArc((1.341640786, -18), (1.799302724, -16.749903013), (1.272792206, -15.527207794))
            ThreePointArc((1.272792206, -15.527207794), (1.272792206, -14.749390335), (2.050609665, -14.749390335))
            ThreePointArc((2.050609665, -14.749390335), (2.853462499, -16.282552641), (2.640075756, -18))
            Line((2.640075756, -18), (7, -18))
            Line((7, -18), (7, -3))
            Line((7, -3), (2.640075756, -3))
            ThreePointArc((2.640075756, -3), (2.853462499, -4.717447359), (2.050609665, -6.250609665))
            ThreePointArc((2.050609665, -6.250609665), (1.272792206, -6.250609665), (1.272792206, -5.472792206))
            ThreePointArc((1.272792206, -5.472792206), (1.799302724, -4.250096987), (1.341640786, -3))
            Line((1.341640786, -3), (-1.341640786, -3))
            ThreePointArc((-1.341640786, -3), (-1.799302724, -4.250096987), (-1.272792206, -5.472792206))
            ThreePointArc((-1.272792206, -5.472792206), (-1.272792206, -6.250609665), (-2.050609665, -6.250609665))
            ThreePointArc((-2.050609665, -6.250609665), (-2.853462499, -4.717447359), (-2.640075756, -3))
            Line((-2.640075756, -3), (-7, -3))
            Line((-7, -3), (-7, -18))
            Line((-7, -18), (-2.640075756, -18))
            ThreePointArc((-2.640075756, -18), (-2.853462499, -16.282552641), (-2.050609665, -14.749390335))
            ThreePointArc((-2.050609665, -14.749390335), (-1.272792206, -14.749390335), (-1.272792206, -15.527207794))
            ThreePointArc((-1.272792206, -15.527207794), (-1.799302724, -16.749903013), (-1.341640786, -18))
        make_face(mode=Mode.SUBTRACT)
    extrude(amount=MEMBER_1_4_DEPTH)

    # Member 1 4 end butt 1
    split(bisect_by=Plane(origin=(-567.5, 1118.5, 0), x_dir=(1, 0, 0), z_dir=(0, -1, 0)), keep=Keep.TOP)

    # Member 1 4 end butt 2
    split(bisect_by=Plane(origin=(-567.5, -1118.5, 0), x_dir=(-1, 0, 0), z_dir=(0, 1, 0)), keep=Keep.TOP)


with BuildPart() as body_5:
    # 草图2 → 凸台-拉伸1 (new body)
    with BuildSketch(Plane.XY.offset(9).offset(EXTRUDE_START)):
        Rectangle(SKETCH_2_W, SKETCH_2_H)
    extrude(amount=-EXTRUDE_1_DEPTH)


solid = Compound([part.part, body_2.part, body_3.part, body_4.part, body_5.part])
